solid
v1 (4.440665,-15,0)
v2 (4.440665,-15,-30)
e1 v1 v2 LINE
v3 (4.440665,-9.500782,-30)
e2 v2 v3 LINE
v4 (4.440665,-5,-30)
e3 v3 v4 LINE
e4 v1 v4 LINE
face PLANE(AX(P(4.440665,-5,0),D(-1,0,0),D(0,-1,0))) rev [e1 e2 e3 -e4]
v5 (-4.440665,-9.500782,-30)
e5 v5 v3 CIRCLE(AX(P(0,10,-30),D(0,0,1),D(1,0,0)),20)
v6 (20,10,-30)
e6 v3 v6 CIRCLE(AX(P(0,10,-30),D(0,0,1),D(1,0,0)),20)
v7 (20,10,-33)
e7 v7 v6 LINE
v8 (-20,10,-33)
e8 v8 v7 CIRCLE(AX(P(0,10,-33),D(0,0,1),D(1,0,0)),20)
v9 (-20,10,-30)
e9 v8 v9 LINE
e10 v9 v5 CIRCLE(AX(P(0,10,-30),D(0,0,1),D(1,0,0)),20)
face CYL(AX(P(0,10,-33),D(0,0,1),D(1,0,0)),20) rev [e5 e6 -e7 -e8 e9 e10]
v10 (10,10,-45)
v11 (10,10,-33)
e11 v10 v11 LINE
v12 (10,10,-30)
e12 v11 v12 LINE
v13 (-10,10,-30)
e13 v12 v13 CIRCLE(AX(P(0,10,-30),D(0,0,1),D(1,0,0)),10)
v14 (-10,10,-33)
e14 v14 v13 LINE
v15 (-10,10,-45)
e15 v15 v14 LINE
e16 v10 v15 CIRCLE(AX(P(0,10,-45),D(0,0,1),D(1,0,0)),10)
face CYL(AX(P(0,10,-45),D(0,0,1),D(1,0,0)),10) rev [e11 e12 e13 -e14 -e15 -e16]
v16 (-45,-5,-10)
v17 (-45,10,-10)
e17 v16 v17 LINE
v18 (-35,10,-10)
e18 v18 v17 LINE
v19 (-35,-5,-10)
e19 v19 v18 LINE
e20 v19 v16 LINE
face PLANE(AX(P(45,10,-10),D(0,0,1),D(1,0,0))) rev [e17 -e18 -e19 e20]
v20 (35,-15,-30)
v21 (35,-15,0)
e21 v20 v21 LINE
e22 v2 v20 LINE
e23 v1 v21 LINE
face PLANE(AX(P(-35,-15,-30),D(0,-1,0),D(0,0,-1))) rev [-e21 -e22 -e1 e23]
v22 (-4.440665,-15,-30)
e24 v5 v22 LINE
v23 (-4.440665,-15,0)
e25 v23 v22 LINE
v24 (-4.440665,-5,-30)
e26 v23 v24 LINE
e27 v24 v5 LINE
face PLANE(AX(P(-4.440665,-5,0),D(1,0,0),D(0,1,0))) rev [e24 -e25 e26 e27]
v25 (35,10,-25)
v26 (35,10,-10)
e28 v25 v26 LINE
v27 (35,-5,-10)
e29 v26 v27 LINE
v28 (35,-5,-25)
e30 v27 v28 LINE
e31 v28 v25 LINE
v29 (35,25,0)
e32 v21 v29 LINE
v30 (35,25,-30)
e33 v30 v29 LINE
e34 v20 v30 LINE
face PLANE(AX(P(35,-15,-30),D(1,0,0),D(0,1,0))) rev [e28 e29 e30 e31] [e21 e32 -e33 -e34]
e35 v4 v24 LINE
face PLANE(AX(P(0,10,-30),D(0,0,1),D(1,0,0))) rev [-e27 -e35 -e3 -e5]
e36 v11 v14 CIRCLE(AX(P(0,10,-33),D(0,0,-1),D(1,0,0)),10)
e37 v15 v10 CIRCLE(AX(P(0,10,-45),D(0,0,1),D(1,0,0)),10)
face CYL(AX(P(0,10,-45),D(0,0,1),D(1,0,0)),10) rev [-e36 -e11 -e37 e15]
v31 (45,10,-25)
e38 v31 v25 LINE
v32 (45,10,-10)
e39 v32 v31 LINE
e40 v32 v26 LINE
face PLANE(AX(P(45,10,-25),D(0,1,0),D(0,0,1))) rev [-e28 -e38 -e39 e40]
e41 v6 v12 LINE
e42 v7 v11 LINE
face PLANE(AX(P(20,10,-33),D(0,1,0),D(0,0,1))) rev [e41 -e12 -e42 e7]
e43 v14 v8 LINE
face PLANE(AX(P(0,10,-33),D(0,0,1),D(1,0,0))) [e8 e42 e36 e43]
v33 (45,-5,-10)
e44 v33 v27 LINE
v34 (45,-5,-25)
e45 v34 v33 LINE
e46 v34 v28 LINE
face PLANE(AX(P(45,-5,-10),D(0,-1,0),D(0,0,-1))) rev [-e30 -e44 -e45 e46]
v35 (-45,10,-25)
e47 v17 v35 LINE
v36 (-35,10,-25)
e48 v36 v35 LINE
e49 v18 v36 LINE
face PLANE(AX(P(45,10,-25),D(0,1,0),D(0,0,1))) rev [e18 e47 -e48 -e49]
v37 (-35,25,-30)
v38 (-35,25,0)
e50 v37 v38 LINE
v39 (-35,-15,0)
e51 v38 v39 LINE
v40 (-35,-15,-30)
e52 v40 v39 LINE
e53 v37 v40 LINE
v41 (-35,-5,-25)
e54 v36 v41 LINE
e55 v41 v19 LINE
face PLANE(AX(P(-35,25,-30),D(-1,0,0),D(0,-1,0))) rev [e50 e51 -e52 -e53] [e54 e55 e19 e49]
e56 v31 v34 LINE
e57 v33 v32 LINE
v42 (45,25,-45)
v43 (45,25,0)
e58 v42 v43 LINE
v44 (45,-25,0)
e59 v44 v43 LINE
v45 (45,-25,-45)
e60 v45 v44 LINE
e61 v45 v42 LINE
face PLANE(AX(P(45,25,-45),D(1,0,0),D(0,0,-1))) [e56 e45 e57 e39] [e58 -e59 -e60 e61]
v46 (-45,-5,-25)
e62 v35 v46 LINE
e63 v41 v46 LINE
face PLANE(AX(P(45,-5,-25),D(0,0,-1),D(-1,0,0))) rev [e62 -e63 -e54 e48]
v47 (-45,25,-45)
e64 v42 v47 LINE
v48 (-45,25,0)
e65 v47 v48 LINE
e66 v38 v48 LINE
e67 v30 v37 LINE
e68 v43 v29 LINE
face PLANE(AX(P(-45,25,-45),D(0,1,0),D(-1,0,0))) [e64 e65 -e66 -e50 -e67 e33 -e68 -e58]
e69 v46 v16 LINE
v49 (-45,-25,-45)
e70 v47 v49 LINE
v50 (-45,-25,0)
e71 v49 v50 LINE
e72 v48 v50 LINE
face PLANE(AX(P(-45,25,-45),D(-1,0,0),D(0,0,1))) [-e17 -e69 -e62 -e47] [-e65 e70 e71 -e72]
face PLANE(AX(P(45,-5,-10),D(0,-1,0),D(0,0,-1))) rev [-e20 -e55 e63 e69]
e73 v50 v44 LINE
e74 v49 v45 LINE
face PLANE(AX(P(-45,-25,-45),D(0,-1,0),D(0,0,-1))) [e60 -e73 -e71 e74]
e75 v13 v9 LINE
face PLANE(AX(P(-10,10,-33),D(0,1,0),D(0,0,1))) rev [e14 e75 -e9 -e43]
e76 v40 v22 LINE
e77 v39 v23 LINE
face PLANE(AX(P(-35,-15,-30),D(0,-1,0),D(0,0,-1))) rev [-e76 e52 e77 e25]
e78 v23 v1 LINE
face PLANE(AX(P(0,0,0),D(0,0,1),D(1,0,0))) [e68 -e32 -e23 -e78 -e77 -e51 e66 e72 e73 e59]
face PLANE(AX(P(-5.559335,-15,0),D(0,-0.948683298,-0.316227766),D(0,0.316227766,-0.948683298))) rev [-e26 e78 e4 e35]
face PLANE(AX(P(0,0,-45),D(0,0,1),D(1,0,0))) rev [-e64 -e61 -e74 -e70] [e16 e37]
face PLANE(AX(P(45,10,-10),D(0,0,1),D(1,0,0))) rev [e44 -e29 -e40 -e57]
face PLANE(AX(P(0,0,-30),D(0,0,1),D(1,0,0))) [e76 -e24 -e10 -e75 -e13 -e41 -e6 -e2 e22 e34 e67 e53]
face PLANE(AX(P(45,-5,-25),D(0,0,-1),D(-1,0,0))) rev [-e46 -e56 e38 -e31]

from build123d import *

# Parameters (mm, degrees)
BLOCK_PROFILE_SKETCH_90X50_W   = 90
BLOCK_PROFILE_SKETCH_90X50_H   = 50
BASE_BLOCK_90X50X45_DEPTH      = 45
POCKET_SKETCH_W                = 70
POCKET_SKETCH_H                = 40
INNER_POCKET_30_DEEP_DEPTH     = 30
BORE_SKETCH_R                  = 10
GUIDE_BORE_CUT_DEPTH           = 60.581876439
SIDE_WINDOW_SKETCH_W           = 15
SIDE_WINDOW_SKETCH_H           = 15
SIDE_WINDOWS_15X15_DEPTH       = 104.682206767
RIB_SKETCH_W                   = 8.881329336
RIB_SKETCH_H                   = 10
INTERNAL_RIB_DEPTH             = 30
ARC_RELIEF_GROOVE_3_DEEP_DEPTH = 3
RIB_TRIM_CUT_10_DEEP_DEPTH     = 10


with BuildPart() as part:
    # Block Profile Sketch 90x50 → Base Block 90x50x45 (new body)
    with BuildSketch(Plane.XY):
        Rectangle(BLOCK_PROFILE_SKETCH_90X50_W, BLOCK_PROFILE_SKETCH_90X50_H)
    extrude(amount=-BASE_BLOCK_90X50X45_DEPTH)

    # Pocket Sketch → Inner Pocket 30 Deep (cut)
    with BuildSketch(Plane.XY):
        with Locations((0, 5)):
            Rectangle(POCKET_SKETCH_W, POCKET_SKETCH_H)
    extrude(amount=-INNER_POCKET_30_DEEP_DEPTH, mode=Mode.SUBTRACT)

    # Bore Sketch → Guide Bore Cut (cut, through all)
    with BuildSketch(Plane.XY.offset(-30)):
        with Locations((0, 10)):
            Circle(BORE_SKETCH_R)
    extrude(amount=-GUIDE_BORE_CUT_DEPTH, mode=Mode.SUBTRACT)

    # Side Window Sketch → Side Windows 15x15 (cut, through all)
    with BuildSketch(Plane.ZY.offset(45)):
        with Locations((-17.5, 2.5)):
            Rectangle(SIDE_WINDOW_SKETCH_W, SIDE_WINDOW_SKETCH_H)
    extrude(amount=-SIDE_WINDOWS_15X15_DEPTH, mode=Mode.SUBTRACT)

    # Rib Sketch → Internal Rib (add)
    with BuildSketch(Plane.XY.offset(-30)):
        with Locations((0, -10)):
            Rectangle(RIB_SKETCH_W, RIB_SKETCH_H)
    extrude(amount=INTERNAL_RIB_DEPTH)

    # Arc Groove Sketch → Arc Relief Groove 3 Deep (cut)
    with BuildSketch(Plane.XY.offset(-30)):
        with BuildLine():
            Line((20, 10), (10, 10))
            ThreePointArc((10, 10), (0, 0), (-10, 10))
            Line((-10, 10), (-20, 10))
            ThreePointArc((-20, 10), (0, -10), (20, 10))
        make_face()
    extrude(amount=-ARC_RELIEF_GROOVE_3_DEEP_DEPTH, mode=Mode.SUBTRACT)

    # Rib Trim Sketch → Rib Trim Cut 10 Deep (cut)
    with BuildSketch(Plane(origin=(4.440664668, 0, 0), x_dir=(0, 0, -1), z_dir=(1, 0, 0))):
        Polygon((30, -5), (0, -5), (0, -15), align=None)
    extrude(amount=-RIB_TRIM_CUT_10_DEEP_DEPTH, mode=Mode.SUBTRACT)


solid = part.part
